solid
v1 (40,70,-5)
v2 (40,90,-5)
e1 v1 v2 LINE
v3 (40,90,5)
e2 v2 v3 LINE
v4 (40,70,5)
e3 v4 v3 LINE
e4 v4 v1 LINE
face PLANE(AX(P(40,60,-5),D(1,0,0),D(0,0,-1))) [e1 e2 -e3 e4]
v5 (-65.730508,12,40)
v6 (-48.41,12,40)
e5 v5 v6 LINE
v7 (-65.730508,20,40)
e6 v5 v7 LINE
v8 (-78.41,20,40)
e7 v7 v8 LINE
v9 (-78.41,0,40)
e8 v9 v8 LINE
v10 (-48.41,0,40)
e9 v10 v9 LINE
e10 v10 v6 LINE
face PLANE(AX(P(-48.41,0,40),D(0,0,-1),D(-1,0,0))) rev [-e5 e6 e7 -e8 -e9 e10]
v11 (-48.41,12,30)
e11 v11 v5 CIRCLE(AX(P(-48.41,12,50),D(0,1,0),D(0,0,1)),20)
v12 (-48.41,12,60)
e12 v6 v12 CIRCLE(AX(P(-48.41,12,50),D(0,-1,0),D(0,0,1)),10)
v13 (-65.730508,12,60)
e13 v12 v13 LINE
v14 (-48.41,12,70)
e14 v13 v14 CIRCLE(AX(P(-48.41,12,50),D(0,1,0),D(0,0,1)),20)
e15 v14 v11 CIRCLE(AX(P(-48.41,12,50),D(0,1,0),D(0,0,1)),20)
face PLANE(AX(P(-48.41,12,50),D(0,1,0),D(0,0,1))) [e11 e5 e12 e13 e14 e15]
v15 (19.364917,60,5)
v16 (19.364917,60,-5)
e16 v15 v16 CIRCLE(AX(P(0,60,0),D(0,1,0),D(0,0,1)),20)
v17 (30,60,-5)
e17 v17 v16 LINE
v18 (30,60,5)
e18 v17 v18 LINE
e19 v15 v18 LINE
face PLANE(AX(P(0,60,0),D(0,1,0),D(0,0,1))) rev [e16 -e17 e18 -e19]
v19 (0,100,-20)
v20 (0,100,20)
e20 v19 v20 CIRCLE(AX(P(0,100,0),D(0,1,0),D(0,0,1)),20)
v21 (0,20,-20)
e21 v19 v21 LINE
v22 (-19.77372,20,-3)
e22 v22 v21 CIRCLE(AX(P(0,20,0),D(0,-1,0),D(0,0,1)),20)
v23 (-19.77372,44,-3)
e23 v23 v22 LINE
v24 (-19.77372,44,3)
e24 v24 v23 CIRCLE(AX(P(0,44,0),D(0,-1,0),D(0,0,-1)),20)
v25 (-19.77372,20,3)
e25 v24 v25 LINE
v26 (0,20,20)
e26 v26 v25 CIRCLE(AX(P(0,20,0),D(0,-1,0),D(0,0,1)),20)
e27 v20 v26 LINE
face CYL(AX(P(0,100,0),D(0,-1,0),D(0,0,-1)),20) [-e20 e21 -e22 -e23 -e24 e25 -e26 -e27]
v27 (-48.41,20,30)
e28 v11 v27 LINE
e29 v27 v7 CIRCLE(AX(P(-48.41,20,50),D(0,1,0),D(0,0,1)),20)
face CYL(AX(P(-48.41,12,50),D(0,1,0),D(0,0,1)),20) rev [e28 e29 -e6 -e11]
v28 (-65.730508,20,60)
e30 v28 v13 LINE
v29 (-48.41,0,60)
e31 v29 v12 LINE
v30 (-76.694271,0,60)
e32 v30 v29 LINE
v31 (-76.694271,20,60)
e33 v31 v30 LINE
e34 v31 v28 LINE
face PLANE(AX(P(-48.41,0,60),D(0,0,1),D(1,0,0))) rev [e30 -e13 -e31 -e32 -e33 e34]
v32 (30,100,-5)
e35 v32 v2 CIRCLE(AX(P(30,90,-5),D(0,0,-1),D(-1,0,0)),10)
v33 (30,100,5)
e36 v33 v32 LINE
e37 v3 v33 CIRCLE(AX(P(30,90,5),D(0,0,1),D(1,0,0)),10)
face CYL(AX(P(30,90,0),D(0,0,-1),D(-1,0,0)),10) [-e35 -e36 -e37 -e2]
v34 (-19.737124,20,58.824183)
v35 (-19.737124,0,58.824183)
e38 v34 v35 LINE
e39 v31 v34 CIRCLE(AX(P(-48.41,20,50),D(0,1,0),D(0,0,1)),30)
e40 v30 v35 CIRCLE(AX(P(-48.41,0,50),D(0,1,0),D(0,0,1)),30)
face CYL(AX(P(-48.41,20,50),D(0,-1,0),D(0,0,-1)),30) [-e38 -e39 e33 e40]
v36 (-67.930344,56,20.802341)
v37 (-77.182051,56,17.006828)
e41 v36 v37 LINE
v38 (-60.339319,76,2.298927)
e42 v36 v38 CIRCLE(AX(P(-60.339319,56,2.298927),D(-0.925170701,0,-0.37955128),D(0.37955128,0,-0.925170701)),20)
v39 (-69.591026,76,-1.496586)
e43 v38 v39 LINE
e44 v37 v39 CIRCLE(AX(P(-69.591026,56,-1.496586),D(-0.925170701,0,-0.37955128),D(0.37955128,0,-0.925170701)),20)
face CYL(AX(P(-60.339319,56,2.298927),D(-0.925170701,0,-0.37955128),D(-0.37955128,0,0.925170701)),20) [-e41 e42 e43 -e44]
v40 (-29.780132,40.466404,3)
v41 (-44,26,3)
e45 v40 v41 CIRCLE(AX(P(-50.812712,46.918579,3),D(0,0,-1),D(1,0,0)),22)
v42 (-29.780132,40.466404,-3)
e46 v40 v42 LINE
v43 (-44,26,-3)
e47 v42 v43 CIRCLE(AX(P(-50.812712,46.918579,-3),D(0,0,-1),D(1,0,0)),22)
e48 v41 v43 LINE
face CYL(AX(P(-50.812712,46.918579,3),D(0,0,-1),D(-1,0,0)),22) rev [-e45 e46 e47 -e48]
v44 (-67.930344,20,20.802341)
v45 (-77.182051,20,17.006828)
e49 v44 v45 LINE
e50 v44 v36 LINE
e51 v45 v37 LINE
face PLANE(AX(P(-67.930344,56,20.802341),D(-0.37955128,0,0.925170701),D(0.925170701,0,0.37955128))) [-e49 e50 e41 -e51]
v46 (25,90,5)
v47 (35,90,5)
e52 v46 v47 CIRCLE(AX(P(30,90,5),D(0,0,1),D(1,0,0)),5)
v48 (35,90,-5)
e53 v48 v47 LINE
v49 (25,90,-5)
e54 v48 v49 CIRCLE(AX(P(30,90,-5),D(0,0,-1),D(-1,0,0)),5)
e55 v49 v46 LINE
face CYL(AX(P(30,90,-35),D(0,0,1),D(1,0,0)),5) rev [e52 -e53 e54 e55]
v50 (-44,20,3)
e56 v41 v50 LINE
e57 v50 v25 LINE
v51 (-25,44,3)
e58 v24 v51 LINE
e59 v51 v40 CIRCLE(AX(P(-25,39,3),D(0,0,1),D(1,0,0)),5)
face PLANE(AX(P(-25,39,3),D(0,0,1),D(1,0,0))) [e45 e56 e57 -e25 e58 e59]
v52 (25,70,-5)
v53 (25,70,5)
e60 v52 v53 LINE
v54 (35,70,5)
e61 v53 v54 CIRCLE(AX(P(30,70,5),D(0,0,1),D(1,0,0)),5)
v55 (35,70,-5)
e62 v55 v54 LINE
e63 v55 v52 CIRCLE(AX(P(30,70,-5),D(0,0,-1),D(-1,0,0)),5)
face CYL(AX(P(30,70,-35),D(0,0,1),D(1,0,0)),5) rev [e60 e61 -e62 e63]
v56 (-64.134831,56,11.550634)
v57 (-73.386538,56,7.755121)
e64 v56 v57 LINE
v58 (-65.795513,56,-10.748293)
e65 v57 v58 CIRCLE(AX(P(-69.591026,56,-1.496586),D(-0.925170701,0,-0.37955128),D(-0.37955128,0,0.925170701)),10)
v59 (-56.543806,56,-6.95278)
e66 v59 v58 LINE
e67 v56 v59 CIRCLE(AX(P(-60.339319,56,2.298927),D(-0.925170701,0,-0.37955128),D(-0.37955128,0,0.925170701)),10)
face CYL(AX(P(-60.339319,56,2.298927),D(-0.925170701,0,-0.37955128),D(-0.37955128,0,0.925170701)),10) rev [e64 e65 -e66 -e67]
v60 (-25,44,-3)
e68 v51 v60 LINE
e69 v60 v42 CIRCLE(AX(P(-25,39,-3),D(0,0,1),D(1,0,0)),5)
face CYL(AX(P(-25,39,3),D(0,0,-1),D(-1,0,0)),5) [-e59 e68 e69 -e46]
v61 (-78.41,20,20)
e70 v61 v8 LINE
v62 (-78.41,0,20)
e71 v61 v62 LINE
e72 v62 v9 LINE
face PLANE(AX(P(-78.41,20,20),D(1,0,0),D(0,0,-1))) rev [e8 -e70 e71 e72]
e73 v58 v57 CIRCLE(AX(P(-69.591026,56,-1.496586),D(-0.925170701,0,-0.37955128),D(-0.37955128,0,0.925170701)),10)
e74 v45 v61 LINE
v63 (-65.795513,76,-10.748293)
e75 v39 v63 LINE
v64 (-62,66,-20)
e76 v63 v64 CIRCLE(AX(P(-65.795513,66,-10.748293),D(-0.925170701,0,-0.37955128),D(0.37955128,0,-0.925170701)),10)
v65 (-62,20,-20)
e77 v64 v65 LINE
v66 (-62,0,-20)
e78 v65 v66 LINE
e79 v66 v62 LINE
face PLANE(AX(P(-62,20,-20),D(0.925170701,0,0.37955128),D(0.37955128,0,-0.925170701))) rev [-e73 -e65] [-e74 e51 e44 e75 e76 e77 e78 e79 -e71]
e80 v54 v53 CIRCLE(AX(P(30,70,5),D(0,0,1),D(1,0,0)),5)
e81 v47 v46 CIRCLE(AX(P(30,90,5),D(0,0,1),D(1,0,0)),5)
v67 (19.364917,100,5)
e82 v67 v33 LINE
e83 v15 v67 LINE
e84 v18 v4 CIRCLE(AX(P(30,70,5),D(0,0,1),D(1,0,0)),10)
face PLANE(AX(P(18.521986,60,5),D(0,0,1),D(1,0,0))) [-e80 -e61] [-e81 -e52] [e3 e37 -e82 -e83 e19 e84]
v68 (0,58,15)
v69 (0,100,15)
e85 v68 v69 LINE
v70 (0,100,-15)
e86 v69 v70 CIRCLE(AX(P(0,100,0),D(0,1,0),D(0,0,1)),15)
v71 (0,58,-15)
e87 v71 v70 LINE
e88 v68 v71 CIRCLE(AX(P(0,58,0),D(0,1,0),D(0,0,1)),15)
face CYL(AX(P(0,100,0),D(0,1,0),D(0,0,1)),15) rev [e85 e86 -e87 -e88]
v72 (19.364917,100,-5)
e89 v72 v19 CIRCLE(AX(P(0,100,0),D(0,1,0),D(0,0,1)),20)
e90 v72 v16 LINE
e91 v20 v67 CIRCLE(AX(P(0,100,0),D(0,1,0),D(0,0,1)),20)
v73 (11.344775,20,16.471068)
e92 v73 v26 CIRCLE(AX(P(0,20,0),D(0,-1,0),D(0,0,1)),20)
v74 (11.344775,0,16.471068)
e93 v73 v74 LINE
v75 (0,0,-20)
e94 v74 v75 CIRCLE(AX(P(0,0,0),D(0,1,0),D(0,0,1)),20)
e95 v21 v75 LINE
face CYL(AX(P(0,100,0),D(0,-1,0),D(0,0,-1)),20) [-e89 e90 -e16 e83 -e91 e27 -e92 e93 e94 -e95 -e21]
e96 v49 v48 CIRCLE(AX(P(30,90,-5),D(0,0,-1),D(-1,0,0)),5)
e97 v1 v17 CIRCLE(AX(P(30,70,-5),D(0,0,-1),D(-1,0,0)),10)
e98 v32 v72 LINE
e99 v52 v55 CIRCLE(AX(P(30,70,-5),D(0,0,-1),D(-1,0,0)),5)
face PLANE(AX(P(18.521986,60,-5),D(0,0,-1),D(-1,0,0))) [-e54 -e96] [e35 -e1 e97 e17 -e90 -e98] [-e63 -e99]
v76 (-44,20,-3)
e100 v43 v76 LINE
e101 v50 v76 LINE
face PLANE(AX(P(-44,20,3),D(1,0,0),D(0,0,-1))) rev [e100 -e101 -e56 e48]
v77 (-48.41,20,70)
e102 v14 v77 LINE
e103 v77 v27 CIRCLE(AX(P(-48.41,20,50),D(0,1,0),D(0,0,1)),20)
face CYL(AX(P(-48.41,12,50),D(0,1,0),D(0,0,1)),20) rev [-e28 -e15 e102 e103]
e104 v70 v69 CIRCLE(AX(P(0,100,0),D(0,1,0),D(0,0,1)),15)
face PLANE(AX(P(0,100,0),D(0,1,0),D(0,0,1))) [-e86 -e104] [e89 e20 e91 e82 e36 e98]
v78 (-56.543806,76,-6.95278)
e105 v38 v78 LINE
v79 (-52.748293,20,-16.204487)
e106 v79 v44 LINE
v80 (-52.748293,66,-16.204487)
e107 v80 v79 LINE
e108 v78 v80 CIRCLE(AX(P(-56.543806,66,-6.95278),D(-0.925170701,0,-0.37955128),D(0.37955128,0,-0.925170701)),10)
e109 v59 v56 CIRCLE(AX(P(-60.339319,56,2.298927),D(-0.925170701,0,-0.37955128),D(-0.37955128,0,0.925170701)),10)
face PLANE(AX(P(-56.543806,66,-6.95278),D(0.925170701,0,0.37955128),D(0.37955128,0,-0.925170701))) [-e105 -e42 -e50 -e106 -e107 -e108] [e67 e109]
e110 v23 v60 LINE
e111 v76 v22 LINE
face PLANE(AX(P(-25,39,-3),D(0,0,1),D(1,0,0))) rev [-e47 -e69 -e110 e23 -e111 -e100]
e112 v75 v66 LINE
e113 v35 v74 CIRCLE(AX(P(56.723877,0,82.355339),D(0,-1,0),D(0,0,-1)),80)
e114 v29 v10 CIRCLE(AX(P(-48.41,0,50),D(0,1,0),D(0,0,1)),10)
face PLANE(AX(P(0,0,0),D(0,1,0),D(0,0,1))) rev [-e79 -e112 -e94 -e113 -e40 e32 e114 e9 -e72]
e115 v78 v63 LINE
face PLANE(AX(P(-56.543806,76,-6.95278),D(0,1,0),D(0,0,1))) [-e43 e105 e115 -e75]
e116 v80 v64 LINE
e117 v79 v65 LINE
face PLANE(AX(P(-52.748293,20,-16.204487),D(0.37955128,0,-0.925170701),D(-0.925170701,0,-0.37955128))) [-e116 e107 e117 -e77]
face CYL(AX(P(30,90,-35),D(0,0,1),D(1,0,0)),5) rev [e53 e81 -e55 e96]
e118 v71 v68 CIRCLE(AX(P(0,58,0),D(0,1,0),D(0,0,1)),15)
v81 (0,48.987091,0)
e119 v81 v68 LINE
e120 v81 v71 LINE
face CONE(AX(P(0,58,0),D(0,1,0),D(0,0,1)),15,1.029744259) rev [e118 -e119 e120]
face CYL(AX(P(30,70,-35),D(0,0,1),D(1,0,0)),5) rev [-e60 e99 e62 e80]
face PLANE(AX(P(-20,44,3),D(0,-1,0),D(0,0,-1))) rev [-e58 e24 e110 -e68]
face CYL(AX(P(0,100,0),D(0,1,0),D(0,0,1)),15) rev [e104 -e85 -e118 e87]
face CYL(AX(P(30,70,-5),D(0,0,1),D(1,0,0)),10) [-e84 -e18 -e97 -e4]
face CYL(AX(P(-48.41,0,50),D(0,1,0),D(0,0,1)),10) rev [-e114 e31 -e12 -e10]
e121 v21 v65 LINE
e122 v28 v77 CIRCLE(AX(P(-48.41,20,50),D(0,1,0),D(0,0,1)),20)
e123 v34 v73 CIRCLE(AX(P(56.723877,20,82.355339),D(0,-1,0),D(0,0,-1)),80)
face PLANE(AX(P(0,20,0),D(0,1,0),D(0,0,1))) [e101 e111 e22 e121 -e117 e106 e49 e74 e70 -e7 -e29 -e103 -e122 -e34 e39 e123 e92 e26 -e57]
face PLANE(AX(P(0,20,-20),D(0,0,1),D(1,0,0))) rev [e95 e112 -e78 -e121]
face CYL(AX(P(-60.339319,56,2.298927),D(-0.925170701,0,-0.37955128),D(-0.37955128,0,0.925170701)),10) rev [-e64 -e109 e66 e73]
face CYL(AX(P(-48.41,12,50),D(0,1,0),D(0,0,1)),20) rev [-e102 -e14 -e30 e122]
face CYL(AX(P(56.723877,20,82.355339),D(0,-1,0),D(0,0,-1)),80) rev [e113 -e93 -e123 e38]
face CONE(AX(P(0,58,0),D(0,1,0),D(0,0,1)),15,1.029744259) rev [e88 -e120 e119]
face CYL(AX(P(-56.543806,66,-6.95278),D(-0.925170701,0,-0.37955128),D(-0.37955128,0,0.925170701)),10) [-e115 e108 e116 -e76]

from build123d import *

# Parameters (mm, degrees)
COLUMN_PROFILE_SKETCH_R   = 20
COLUMN_BOSS_DEPTH         = 100
BASE_ARM_PLATE_DEPTH      = 20
COLUMN_BORE_30_D          = 30
COLUMN_BORE_30_DEPTH      = 42
COLUMN_BORE_30_TIP        = 9.012909285
HOOK_GUIDE_BLOCK_SKETCH_R = 10
HOOK_GUIDE_BLOCK_DEPTH    = 10
HOOK_SLOT_CUT_DEPTH       = 138.652199764
HOOK_RECESS_SKETCH_R      = 20
HOOK_RECESS_20_DEPTH      = 8
CLAMP_LUG_SKETCH_W        = 21.478013603
CLAMP_LUG_SKETCH_H        = 10
CLAMP_LUG_DEPTH           = 40
CLAMP_LUG_FILLET_R10_R    = 10
CLAMP_HOLES_SKETCH_R      = 5
CLAMP_HOLES_2X_10_DEPTH   = 40
EYE_LUG_DEPTH             = 3


with BuildPart() as part:
    # Column Profile Sketch → Column Boss (new body)
    with BuildSketch(Plane(origin=(0, 0, 0), x_dir=(1, 0, 0), z_dir=(0, 1, 0))):
        with Locations(Location((0, 0, 0), (0, 0, 270))):
            Circle(COLUMN_PROFILE_SKETCH_R)
    extrude(amount=COLUMN_BOSS_DEPTH)

    # Base Arm Profile Sketch → Base Arm Plate (add)
    with BuildSketch(Plane(origin=(0, 0, 0), x_dir=(1, 0, 0), z_dir=(0, 1, 0))):
        with BuildLine():
            Line((0, 20), (-62, 20))
            Line((-62, 20), (-78.41, -20))
            Line((-78.41, -20), (-78.41, -50))
            ThreePointArc((-78.41, -50), (-52.871711259, -79.666363657), (-19.737124491, -58.82418325))
            ThreePointArc((-19.737124491, -58.82418325), (-7.771853725, -35.023523327), (11.344775373, -16.471067717))
            ThreePointArc((11.344775373, -16.471067717), (-19.097399749, -5.9404817), (0, 20))
        make_face()
    extrude(amount=BASE_ARM_PLATE_DEPTH)

    # Column Bore Ø30
    with Locations(Plane.ZX.offset(100)):
        with Locations((0, 0)):
            Hole(COLUMN_BORE_30_D / 2, depth=COLUMN_BORE_30_DEPTH)
            with Locations((0, 0, -(COLUMN_BORE_30_DEPTH + COLUMN_BORE_30_TIP / 2))):  # 118° drill point
                Cone(0, COLUMN_BORE_30_D / 2, COLUMN_BORE_30_TIP, mode=Mode.SUBTRACT)

    # Hook Guide Block Sketch → Hook Guide Block (add)
    with BuildSketch(Plane(origin=(-60.091325676, 0, -24.652466359), x_dir=(-0.3795512800466907, 0, 0.9251707009060105), z_dir=(-0.9251707009060105, 0, -0.3795512800466907))):
        with BuildLine():
            Line((5.028765345, 20), (5.028765345, 66))
            ThreePointArc((5.028765345, 66), (7.957697533, 73.071067812), (15.028765345, 76))
            Line((15.028765345, 76), (25.028765345, 76))
            ThreePointArc((25.028765345, 76), (39.170900969, 70.142135624), (45.028765345, 56))
            Line((45.028765345, 56), (45.028765345, 20))
            Line((45.028765345, 20), (5.028765345, 20))
        make_face()
        with Locations((25.028765345, 56)):
            Circle(HOOK_GUIDE_BLOCK_SKETCH_R, mode=Mode.SUBTRACT)
    extrude(amount=-HOOK_GUIDE_BLOCK_DEPTH)

    # Hook Slot Sketch → Hook Slot Cut (cut, through all)
    with BuildSketch(Plane(origin=(0, 20, 0), x_dir=(1, 0, 0), z_dir=(0, 1, 0))):
        with BuildLine():
            Line((-48.41, -40), (-78.41, -40))
            Line((-78.41, -40), (-78.41, -60))
            Line((-78.41, -60), (-48.41, -60))
            ThreePointArc((-48.41, -60), (-38.41, -50), (-48.41, -40))
        make_face()
    extrude(amount=-HOOK_SLOT_CUT_DEPTH, mode=Mode.SUBTRACT)

    # Hook Recess Sketch → Hook Recess Ø20 (cut)
    with BuildSketch(Plane(origin=(0, 20, 0), x_dir=(1, 0, 0), z_dir=(0, 1, 0))):
        with Locations((-48.41, -50)):
            Circle(HOOK_RECESS_SKETCH_R)
    extrude(amount=-HOOK_RECESS_20_DEPTH, mode=Mode.SUBTRACT)

    # Clamp Lug Sketch → Clamp Lug (add)
    with BuildSketch(Plane(origin=(0, 100, 0), x_dir=(1, 0, 0), z_dir=(0, 1, 0))):
        with Locations((29.260993199, 0)):
            Rectangle(CLAMP_LUG_SKETCH_W, CLAMP_LUG_SKETCH_H)
    extrude(amount=-CLAMP_LUG_DEPTH)

    # Clamp Lug Fillet R10
    clamp_lug_fillet_r10_edges = [part.edges().sort_by_distance(p)[0] for p in [
        (40, 60, 0),
        (40, 100, 0),
    ]]
    fillet(clamp_lug_fillet_r10_edges, radius=CLAMP_LUG_FILLET_R10_R)

    # Clamp Holes Sketch → Clamp Holes 2xØ10 (cut)
    with BuildSketch(Plane.XY.offset(5)):
        with Locations((30, 90)):
            Circle(CLAMP_HOLES_SKETCH_R)
        with Locations((30, 70)):
            Circle(CLAMP_HOLES_SKETCH_R)
    extrude(amount=-CLAMP_HOLES_2X_10_DEPTH, mode=Mode.SUBTRACT)

    # Eye Lug Sketch → Eye Lug (add, symmetric)
    with BuildSketch(Plane.XY):
        with BuildLine():
            Line((-44, 20), (-44, 26))
            ThreePointArc((-44, 26), (-35.12324798, 31.496493808), (-29.780131863, 40.466403549))
            ThreePointArc((-29.780131863, 40.466403549), (-27.972203076, 43.020697561), (-25, 44))
            Line((-25, 44), (-20, 44))
            Line((-20, 44), (-17, 44))
            Line((-17, 44), (-17, 20))
            Line((-17, 20), (-44, 20))
        make_face()
    extrude(amount=EYE_LUG_DEPTH, both=True)


solid = part.part
